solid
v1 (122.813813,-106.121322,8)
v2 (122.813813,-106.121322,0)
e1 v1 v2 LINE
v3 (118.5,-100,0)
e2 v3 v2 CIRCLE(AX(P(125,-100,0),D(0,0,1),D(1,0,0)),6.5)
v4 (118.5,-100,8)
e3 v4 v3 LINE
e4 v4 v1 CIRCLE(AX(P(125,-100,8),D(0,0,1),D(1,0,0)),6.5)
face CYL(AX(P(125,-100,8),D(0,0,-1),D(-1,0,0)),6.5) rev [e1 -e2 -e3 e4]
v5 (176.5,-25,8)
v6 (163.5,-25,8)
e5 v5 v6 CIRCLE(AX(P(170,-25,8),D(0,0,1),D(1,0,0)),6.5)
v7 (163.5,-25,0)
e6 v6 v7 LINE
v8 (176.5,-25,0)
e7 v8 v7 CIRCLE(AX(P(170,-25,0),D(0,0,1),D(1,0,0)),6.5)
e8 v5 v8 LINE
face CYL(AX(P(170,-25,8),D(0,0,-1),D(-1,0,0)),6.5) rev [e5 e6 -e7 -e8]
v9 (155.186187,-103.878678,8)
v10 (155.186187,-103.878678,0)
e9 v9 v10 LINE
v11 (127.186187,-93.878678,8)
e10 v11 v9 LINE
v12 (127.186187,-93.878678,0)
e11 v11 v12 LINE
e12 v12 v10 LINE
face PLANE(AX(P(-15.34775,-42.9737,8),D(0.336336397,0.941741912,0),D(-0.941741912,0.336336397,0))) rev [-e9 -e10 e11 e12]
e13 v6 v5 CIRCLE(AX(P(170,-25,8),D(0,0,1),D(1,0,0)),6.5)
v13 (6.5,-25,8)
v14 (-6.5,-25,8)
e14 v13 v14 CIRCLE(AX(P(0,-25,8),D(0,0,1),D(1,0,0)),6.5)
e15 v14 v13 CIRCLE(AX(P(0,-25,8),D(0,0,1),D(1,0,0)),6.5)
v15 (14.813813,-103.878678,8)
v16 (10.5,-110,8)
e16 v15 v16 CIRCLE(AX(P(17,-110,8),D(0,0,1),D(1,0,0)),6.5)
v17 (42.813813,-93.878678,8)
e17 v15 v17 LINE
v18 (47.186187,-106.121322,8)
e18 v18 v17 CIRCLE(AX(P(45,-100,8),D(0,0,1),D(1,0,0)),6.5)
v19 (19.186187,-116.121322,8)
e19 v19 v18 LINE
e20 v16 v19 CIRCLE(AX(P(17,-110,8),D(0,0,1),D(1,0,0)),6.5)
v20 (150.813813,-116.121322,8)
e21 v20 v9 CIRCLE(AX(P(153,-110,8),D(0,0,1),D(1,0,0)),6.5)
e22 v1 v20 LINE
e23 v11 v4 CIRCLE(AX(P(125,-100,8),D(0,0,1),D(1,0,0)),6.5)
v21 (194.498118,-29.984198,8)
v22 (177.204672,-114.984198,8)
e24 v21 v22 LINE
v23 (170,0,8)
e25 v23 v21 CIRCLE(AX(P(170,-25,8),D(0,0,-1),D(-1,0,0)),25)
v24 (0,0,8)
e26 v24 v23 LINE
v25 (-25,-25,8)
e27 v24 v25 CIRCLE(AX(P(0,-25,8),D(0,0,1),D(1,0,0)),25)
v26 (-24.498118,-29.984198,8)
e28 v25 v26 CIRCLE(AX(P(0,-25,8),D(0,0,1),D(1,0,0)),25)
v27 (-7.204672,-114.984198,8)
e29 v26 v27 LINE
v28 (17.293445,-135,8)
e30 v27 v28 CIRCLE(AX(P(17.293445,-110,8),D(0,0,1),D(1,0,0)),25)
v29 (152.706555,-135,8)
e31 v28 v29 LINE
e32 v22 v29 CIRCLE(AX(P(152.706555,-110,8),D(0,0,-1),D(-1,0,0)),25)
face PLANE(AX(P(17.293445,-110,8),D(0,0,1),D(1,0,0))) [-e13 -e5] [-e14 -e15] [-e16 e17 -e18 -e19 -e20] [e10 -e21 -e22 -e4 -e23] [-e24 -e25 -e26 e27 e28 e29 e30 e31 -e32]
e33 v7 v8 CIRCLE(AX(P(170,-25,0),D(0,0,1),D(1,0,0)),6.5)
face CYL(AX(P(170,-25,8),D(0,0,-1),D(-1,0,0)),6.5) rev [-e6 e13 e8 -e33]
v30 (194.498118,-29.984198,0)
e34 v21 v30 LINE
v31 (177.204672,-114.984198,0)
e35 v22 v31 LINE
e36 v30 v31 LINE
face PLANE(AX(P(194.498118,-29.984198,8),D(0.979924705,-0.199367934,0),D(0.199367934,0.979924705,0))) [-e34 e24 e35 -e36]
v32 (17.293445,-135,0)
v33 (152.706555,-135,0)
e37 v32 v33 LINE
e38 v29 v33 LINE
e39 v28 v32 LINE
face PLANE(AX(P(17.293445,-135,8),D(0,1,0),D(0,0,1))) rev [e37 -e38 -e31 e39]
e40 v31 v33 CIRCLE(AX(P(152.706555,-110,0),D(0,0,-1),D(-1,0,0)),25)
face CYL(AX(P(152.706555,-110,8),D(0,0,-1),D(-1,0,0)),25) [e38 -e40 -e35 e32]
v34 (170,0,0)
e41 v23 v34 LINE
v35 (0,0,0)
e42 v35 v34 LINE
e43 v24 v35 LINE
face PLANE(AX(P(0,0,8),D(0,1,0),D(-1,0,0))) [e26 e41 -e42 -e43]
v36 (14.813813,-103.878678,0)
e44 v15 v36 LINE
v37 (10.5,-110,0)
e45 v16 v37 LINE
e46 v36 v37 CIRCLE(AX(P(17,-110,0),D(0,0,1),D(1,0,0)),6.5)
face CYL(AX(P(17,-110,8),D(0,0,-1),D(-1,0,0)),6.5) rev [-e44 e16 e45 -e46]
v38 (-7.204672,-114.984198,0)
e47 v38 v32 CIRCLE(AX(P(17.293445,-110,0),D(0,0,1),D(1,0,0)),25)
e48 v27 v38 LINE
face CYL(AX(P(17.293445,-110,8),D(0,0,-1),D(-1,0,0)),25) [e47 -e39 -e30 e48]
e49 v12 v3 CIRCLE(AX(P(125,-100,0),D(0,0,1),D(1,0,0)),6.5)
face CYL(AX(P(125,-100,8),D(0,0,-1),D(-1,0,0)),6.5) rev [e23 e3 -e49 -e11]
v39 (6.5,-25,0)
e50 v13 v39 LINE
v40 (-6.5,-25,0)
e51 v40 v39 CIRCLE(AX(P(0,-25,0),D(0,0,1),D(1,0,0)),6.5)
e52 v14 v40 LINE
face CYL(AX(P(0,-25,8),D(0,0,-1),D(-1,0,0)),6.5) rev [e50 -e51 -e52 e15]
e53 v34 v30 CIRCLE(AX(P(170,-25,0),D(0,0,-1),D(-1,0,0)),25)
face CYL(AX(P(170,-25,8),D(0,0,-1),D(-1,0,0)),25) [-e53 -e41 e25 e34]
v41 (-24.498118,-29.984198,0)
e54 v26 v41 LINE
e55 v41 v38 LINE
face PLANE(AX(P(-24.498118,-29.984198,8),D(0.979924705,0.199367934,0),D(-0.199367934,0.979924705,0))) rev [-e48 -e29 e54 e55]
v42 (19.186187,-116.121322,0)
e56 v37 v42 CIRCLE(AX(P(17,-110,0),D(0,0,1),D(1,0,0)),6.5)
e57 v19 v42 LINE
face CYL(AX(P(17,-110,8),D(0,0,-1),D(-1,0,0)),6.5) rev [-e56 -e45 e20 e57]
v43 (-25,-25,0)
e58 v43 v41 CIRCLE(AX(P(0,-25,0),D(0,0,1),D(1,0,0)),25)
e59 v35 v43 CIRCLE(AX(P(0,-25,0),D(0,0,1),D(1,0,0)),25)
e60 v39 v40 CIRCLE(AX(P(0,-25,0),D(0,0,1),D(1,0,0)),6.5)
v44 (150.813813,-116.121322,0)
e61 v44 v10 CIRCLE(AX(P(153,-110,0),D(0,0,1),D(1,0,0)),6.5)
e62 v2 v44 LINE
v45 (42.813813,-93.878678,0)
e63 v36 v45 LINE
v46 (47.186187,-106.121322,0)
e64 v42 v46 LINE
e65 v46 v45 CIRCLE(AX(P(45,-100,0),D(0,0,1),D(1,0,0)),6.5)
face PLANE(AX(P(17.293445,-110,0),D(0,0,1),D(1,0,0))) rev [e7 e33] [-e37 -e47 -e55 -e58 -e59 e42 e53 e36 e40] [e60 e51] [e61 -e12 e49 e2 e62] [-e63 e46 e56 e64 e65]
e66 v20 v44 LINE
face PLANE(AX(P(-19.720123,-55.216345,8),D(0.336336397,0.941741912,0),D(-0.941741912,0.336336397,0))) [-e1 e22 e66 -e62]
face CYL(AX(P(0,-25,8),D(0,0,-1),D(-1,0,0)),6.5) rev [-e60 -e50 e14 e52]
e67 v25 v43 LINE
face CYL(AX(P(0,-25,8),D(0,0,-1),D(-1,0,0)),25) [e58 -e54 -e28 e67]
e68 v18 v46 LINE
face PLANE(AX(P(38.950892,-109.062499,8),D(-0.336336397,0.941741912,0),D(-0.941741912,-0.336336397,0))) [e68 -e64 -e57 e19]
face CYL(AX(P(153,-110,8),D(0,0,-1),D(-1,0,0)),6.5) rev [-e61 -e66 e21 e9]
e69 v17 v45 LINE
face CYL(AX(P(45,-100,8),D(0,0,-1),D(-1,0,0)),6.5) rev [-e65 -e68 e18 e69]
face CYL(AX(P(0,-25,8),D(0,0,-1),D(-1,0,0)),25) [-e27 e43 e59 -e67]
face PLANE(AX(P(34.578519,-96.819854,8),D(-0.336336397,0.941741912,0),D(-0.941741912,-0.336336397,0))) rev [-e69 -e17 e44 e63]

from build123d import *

# Parameters (mm, degrees)
SKETCH1_R           = 6.5
BOSS_EXTRUDE1_DEPTH = 8


with BuildPart() as part:
    # Sketch1 → Boss-Extrude1 (new body)
    with BuildSketch(Plane.XY):
        with BuildLine():
            Line((0, 0), (170, 0))
            ThreePointArc((170, 0), (189.359816102, -9.182366786), (194.498117616, -29.98419836))
            Line((194.498117616, -29.98419836), (177.204672165, -114.98419836))
            ThreePointArc((177.204672165, -114.98419836), (168.524187763, -129.359816102), (152.706554549, -135))
            Line((152.706554549, -135), (17.293445451, -135))
            ThreePointArc((17.293445451, -135), (1.475812237, -129.359816102), (-7.204672165, -114.98419836))
            Line((-7.204672165, -114.98419836), (-24.498117616, -29.98419836))
            ThreePointArc((-24.498117616, -29.98419836), (-19.359816102, -9.182366786), (0, 0))
        make_face()
        with Locations((0, -25)):
            Circle(SKETCH1_R, mode=Mode.SUBTRACT)
        with Locations((170, -25)):
            Circle(SKETCH1_R, mode=Mode.SUBTRACT)
        with BuildLine():
            Line((14.81381342, -103.878677575), (42.81381342, -93.878677575))
            ThreePointArc((42.81381342, -93.878677575), (51.121322425, -97.81381342), (47.18618658, -106.121322425))
            Line((47.18618658, -106.121322425), (19.18618658, -116.121322425))
            ThreePointArc((19.18618658, -116.121322425), (10.878677575, -112.18618658), (14.81381342, -103.878677575))
        make_face(mode=Mode.SUBTRACT)
        with BuildLine():
            Line((127.18618658, -93.878677575), (155.18618658, -103.878677575))
            ThreePointArc((155.18618658, -103.878677575), (159.121322425, -112.18618658), (150.81381342, -116.121322425))
            Line((150.81381342, -116.121322425), (122.81381342, -106.121322425))
            ThreePointArc((122.81381342, -106.121322425), (118.878677575, -97.81381342), (127.18618658, -93.878677575))
        make_face(mode=Mode.SUBTRACT)
    extrude(amount=BOSS_EXTRUDE1_DEPTH)


solid = part.part
